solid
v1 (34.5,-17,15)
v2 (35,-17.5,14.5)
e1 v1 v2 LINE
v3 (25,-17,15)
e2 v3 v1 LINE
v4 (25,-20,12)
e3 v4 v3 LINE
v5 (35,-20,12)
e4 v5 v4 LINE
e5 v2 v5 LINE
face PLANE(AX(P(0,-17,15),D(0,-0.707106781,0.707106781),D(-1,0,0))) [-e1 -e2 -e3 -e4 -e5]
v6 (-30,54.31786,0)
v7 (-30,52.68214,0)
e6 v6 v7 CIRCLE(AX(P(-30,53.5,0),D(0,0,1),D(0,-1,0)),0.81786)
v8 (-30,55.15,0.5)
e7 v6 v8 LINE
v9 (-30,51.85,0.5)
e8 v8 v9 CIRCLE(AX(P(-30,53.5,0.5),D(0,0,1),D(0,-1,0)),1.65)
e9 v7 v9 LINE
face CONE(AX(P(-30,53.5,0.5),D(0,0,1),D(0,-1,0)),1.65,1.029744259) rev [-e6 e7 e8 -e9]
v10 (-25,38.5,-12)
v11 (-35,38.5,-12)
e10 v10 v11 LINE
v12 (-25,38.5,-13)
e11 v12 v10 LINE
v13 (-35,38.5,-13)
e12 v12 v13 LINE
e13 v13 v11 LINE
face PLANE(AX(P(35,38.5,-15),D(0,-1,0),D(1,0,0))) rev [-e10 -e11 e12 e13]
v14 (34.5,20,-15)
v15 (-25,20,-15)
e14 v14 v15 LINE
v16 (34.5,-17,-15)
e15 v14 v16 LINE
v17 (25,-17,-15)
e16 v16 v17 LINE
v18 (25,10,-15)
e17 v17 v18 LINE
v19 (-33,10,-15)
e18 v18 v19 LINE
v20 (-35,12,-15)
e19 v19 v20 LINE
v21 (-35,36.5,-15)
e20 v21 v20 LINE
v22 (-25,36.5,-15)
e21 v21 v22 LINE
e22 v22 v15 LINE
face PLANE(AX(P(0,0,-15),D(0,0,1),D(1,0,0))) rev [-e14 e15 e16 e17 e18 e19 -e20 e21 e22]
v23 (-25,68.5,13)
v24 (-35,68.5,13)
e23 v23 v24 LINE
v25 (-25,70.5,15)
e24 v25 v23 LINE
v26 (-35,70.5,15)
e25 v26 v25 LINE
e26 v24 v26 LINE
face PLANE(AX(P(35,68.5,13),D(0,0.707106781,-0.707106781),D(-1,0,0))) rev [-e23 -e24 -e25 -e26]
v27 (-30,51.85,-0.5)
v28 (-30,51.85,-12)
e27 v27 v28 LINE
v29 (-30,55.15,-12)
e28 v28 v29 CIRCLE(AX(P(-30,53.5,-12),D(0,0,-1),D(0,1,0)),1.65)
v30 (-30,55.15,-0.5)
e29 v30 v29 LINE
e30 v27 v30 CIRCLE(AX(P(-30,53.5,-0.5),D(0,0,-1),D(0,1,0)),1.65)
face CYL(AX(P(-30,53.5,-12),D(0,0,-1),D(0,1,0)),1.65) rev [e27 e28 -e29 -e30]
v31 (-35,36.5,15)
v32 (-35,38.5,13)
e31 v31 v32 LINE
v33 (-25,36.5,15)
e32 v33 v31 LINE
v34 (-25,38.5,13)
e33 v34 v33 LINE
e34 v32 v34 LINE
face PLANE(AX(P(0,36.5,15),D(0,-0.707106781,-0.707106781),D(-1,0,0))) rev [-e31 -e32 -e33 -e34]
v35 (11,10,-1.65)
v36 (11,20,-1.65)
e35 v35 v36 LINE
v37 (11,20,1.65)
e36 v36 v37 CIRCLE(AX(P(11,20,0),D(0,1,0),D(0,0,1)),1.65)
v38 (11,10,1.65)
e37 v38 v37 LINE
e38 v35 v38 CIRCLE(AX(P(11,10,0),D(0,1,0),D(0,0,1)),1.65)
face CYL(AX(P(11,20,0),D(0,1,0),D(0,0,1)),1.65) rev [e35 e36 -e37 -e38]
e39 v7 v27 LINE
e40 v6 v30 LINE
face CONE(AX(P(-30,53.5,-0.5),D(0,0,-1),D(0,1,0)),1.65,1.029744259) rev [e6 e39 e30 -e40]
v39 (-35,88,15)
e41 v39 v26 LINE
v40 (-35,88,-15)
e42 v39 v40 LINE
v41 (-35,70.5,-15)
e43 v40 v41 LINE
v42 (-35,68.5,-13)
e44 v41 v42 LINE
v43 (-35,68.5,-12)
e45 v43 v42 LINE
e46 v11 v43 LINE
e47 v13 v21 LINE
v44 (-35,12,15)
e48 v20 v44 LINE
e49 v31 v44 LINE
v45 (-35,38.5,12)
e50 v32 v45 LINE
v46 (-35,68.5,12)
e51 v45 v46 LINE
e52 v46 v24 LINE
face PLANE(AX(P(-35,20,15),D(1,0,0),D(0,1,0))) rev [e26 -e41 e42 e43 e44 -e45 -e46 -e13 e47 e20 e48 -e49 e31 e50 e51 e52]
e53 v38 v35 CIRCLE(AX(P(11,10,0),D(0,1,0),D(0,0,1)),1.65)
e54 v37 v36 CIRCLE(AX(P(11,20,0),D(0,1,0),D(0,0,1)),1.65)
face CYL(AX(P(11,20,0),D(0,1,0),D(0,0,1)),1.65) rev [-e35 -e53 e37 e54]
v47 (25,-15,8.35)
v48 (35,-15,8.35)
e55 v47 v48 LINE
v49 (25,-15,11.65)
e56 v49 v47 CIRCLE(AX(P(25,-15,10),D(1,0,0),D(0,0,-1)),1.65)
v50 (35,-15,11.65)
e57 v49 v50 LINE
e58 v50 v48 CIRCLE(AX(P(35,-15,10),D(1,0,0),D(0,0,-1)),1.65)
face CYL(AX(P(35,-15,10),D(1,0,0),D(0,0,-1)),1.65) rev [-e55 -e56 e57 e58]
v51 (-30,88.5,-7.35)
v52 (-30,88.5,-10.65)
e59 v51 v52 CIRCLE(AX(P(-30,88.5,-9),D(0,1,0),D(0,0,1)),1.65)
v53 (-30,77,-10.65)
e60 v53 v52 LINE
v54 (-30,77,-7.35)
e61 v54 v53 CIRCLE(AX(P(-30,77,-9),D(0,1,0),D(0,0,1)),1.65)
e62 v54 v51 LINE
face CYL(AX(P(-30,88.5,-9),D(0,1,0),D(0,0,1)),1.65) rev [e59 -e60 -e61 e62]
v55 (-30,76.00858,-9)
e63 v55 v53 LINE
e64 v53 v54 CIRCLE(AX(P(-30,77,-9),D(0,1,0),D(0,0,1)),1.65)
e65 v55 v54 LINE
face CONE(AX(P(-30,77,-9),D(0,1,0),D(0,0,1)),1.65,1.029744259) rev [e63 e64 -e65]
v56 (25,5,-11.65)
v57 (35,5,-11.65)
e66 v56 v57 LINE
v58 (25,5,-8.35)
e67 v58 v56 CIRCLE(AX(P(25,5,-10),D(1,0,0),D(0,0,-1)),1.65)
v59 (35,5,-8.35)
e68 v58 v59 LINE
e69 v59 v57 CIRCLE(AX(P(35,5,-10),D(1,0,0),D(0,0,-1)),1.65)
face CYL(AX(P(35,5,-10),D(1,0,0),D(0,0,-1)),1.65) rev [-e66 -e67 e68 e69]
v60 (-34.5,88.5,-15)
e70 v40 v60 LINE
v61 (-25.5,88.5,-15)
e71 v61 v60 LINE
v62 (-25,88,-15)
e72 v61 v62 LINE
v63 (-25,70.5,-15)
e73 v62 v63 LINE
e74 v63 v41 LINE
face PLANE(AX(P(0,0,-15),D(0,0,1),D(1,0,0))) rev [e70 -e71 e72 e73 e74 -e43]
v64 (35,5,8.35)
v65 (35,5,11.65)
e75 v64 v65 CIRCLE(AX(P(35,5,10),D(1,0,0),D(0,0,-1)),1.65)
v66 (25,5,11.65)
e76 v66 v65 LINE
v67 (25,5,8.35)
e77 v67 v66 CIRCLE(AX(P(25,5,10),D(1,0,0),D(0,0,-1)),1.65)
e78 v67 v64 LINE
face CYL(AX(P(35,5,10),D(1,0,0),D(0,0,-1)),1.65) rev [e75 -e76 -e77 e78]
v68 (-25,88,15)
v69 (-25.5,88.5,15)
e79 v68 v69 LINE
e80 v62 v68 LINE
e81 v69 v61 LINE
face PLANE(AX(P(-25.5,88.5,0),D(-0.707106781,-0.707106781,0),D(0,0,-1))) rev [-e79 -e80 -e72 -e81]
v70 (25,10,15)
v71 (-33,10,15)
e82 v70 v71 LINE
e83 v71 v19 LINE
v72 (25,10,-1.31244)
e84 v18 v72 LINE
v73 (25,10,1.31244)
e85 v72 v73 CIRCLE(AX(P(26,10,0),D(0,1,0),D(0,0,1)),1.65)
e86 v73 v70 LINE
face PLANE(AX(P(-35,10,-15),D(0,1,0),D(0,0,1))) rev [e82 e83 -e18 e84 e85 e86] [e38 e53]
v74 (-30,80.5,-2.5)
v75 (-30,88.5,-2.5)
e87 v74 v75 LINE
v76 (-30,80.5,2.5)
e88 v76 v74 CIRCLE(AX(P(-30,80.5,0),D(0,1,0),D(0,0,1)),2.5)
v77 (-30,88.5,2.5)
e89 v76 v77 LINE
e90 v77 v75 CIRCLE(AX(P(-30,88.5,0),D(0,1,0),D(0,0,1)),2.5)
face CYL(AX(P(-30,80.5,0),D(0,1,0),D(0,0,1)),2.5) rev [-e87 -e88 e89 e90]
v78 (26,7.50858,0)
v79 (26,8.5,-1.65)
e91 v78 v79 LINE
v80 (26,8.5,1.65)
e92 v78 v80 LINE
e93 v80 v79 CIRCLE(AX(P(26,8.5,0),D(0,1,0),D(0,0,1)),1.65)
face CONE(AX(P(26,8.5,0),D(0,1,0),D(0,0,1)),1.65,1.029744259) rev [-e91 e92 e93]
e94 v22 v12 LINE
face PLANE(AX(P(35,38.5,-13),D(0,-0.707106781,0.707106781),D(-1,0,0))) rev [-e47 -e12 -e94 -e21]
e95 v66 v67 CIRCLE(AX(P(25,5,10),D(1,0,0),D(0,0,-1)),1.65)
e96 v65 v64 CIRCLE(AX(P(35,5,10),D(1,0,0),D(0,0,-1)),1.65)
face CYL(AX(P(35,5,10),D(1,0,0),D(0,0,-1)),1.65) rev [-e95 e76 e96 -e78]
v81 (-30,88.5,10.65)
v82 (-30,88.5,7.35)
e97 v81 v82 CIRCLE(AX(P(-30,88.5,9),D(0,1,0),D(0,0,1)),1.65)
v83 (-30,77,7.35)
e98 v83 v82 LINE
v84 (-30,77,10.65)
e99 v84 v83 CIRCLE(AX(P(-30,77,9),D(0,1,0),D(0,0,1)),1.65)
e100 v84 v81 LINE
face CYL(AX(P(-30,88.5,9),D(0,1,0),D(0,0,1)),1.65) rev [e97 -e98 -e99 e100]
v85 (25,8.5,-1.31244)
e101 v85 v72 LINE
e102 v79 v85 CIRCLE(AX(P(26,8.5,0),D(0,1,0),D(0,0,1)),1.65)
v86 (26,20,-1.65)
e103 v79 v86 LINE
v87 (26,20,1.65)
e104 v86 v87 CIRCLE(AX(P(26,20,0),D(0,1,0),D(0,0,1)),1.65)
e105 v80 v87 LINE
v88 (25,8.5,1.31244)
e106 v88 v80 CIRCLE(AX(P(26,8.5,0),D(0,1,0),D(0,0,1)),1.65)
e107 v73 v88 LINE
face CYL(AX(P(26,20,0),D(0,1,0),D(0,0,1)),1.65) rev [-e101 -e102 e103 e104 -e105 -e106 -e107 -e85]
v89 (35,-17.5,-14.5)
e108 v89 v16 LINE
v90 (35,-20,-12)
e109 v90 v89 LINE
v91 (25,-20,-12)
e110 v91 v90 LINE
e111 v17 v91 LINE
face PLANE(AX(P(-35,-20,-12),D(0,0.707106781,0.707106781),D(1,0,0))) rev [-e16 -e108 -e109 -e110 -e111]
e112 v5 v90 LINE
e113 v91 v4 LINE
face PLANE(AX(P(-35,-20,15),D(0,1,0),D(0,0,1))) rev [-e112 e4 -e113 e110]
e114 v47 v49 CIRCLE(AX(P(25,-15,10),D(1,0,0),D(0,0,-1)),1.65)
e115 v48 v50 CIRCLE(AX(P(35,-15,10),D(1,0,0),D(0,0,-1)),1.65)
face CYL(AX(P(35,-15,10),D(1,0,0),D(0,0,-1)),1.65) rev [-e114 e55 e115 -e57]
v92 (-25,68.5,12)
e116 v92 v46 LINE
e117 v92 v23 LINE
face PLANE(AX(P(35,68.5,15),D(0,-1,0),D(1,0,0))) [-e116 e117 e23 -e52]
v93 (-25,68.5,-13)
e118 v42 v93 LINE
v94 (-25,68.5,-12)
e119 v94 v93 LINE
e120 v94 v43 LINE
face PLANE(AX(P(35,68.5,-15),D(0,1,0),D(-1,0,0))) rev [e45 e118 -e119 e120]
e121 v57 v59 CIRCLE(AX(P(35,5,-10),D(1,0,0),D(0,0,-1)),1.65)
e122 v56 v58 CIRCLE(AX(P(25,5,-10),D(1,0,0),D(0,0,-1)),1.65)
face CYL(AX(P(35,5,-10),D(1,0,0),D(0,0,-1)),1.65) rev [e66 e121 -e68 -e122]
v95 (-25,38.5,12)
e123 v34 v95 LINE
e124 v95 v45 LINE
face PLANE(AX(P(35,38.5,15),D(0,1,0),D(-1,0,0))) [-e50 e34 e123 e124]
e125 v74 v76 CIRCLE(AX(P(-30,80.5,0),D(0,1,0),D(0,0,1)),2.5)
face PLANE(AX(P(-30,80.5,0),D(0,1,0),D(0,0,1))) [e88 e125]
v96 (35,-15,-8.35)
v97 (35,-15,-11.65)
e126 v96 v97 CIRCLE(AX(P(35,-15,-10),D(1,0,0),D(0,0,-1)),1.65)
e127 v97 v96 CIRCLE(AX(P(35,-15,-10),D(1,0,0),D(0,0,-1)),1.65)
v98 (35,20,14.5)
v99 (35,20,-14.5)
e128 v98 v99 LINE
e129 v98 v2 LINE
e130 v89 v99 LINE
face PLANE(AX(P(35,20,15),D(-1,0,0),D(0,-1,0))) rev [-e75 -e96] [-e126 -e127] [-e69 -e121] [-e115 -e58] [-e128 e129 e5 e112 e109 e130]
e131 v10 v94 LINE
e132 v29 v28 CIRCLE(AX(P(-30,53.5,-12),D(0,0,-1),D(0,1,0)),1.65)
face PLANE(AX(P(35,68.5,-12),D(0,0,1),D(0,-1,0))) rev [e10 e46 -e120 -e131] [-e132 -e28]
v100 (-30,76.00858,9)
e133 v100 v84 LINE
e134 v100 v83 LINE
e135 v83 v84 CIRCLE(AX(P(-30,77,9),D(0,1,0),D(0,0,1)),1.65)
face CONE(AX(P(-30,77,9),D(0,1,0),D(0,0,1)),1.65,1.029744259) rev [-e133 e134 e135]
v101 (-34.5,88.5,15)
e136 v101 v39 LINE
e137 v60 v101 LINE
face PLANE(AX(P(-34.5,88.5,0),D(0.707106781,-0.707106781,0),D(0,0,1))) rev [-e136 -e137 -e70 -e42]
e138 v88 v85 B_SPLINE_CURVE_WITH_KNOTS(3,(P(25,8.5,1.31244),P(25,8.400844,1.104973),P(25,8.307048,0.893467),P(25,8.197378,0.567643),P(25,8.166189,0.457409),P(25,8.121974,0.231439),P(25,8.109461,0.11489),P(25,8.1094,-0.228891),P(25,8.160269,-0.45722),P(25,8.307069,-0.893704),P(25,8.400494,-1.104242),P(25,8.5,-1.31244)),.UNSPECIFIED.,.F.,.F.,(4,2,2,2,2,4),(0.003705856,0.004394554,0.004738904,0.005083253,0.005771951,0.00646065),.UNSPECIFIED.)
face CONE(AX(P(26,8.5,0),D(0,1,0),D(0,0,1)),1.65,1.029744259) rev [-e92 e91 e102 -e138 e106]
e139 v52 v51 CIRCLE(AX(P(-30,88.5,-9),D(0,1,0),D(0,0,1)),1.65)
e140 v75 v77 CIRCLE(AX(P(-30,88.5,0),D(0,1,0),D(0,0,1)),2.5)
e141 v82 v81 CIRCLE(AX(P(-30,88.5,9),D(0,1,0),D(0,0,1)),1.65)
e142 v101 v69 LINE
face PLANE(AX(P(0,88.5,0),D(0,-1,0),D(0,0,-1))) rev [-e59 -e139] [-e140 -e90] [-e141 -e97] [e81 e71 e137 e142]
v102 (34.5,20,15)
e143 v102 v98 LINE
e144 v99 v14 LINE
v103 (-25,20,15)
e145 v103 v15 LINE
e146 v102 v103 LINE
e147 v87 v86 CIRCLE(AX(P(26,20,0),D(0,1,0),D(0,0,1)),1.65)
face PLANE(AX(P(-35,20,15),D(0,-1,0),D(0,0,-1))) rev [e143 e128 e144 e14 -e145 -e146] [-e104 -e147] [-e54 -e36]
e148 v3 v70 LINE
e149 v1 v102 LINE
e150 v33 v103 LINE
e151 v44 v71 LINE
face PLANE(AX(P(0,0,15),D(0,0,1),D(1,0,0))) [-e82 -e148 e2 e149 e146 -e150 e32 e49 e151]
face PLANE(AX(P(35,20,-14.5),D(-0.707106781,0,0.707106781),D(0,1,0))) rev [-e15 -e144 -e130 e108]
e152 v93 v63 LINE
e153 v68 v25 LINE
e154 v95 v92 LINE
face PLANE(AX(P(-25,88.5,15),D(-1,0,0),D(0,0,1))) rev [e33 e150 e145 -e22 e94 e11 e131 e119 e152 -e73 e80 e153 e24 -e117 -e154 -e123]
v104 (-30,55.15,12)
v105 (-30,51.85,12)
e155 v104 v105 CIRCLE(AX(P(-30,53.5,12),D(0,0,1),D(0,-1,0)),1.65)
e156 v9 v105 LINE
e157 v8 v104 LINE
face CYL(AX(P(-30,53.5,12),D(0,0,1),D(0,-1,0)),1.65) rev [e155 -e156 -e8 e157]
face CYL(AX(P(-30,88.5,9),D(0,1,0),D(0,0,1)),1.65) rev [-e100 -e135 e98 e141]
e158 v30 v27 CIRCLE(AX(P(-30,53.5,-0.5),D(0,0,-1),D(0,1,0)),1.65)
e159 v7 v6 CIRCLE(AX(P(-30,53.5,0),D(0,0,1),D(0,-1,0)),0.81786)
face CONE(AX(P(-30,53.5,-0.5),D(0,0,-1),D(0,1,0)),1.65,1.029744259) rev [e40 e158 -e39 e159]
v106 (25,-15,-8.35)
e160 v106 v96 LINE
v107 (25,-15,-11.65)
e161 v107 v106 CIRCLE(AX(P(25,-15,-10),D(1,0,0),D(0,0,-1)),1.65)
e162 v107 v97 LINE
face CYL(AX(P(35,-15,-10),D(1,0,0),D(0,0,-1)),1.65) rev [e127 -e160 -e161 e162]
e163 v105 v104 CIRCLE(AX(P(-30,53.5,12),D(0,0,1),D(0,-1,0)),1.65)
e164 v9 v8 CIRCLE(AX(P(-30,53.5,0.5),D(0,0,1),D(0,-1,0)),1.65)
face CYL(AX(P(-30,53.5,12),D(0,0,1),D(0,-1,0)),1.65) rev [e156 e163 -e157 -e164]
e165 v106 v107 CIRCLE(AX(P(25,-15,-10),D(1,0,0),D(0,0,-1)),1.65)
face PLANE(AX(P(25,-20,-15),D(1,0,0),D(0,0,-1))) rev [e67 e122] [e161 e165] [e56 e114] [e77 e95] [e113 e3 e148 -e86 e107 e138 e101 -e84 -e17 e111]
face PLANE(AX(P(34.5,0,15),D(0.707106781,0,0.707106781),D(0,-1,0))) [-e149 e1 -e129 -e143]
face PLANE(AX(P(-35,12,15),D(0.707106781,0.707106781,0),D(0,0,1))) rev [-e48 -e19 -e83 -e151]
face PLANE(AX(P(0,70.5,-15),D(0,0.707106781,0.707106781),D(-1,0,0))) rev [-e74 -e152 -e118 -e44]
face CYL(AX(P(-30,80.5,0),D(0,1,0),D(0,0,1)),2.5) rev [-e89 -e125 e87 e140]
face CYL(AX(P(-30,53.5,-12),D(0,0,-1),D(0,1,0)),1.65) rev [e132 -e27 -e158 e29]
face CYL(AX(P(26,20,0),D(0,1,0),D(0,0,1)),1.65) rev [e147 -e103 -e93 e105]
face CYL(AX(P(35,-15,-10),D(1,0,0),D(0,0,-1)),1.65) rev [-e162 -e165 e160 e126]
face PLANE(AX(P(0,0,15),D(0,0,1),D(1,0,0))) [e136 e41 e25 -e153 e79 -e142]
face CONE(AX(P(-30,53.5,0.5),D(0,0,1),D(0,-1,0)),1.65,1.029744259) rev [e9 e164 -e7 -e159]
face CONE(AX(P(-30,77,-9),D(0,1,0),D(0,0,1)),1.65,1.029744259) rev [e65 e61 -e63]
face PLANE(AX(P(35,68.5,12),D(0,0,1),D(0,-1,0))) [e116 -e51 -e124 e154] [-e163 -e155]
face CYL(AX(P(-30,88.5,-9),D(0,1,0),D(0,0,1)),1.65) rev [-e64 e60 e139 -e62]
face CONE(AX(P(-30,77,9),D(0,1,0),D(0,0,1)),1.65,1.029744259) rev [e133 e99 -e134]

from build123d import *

# Parameters (mm, degrees)
SKETCH1_W             = 70
SKETCH1_H             = 40
BOSS_EXTRUDE1_DEPTH   = 15
SKETCH2_W             = 60
SKETCH2_H             = 30
CUT_EXTRUDE1_DEPTH    = 51.249378106
CHAMFER1_SIZE         = 0.5
M4_TAPPED_HOLE1_D     = 3.3
M4_TAPPED_HOLE1_DEPTH = 11.5
M4_TAPPED_HOLE1_TIP   = 0.991420021
M4_TAPPED_HOLE2_D     = 3.3
CHAMFER3_SIZE         = 3
SKETCH17_W            = 10
SKETCH17_H            = 30
BOSS_EXTRUDE2_DEPTH   = 68.5
CHAMFER4_SIZE         = 0.5
M4_TAPPED_HOLE3_D     = 3.3
M4_TAPPED_HOLE3_DEPTH = 11.5
M4_TAPPED_HOLE3_TIP   = 0.991420021
CHAMFER5_SIZE         = 2
SKETCH20_R            = 2.5
CUT_EXTRUDE2_DEPTH    = 8
SKETCH21_W            = 3
SKETCH21_H            = 30
CUT_EXTRUDE3_DEPTH    = 114.829916981
CHAMFER6_SIZE         = 2


with BuildPart() as part:
    # Sketch1 → Boss-Extrude1 (new, symmetric)
    with BuildSketch(Plane.XY):
        Rectangle(SKETCH1_W, SKETCH1_H)
    extrude(amount=BOSS_EXTRUDE1_DEPTH, both=True)

    # Sketch2 → Cut-Extrude1 (cut, through all)
    with BuildSketch(Plane.XY.offset(15)):
        with Locations((-5, -5)):
            Rectangle(SKETCH2_W, SKETCH2_H)
    extrude(amount=-CUT_EXTRUDE1_DEPTH, mode=Mode.SUBTRACT)

    # Chamfer1
    chamfer1_edges = [part.edges().sort_by_distance(p)[0] for p in [
        (35, 0, 15),
        (35, 0, -15),
    ]]
    chamfer(chamfer1_edges, length=CHAMFER1_SIZE)

    # M4 Tapped Hole1
    with Locations(Plane(origin=(0, 20, 0), x_dir=(1, 0, 0), z_dir=(0, 1, 0))):
        with Locations((11, 0), (26, 0)):
            Hole(M4_TAPPED_HOLE1_D / 2, depth=M4_TAPPED_HOLE1_DEPTH)
            with Locations((0, 0, -(M4_TAPPED_HOLE1_DEPTH + M4_TAPPED_HOLE1_TIP / 2))):  # 118° drill point
                Cone(0, M4_TAPPED_HOLE1_D / 2, M4_TAPPED_HOLE1_TIP, mode=Mode.SUBTRACT)

    # M4 Tapped Hole2 (through all)
    with Locations(Plane(origin=(35, 0, 0), x_dir=(0, 0, -1), z_dir=(1, 0, 0))):
        with Locations((-10, 5), (-10, -15), (10, -15), (10, 5)):
            Hole(M4_TAPPED_HOLE2_D / 2)

    # Chamfer3
    chamfer3_edges = [part.edges().sort_by_distance(p)[0] for p in [
        (29.75, -20, -15),
        (29.75, -20, 15),
    ]]
    chamfer(chamfer3_edges, length=CHAMFER3_SIZE)

    # Sketch17 → Boss-Extrude2 (add)
    with BuildSketch(Plane(origin=(0, 20, 0), x_dir=(1, 0, 0), z_dir=(0, 1, 0))):
        with Locations((-30, 0)):
            Rectangle(SKETCH17_W, SKETCH17_H)
    extrude(amount=BOSS_EXTRUDE2_DEPTH)

    # Chamfer4
    chamfer4_edges = [part.edges().sort_by_distance(p)[0] for p in [
        (-25, 88.5, 0),
        (-35, 88.5, 0),
    ]]
    chamfer(chamfer4_edges, length=CHAMFER4_SIZE)

    # M4 Tapped Hole3
    with Locations(Plane(origin=(0, 88.5, 0), x_dir=(1, 0, 0), z_dir=(0, 1, 0))):
        with Locations((-30, 9), (-30, -9)):
            Hole(M4_TAPPED_HOLE3_D / 2, depth=M4_TAPPED_HOLE3_DEPTH)
            with Locations((0, 0, -(M4_TAPPED_HOLE3_DEPTH + M4_TAPPED_HOLE3_TIP / 2))):  # 118° drill point
                Cone(0, M4_TAPPED_HOLE3_D / 2, M4_TAPPED_HOLE3_TIP, mode=Mode.SUBTRACT)

    # Chamfer5
    chamfer5_edges = [part.edges().sort_by_distance(p)[0] for p in [
        (-35, 10, 0),
    ]]
    chamfer(chamfer5_edges, length=CHAMFER5_SIZE)

    # Sketch20 → Cut-Extrude2 (cut)
    with BuildSketch(Plane(origin=(0, 88.5, 0), x_dir=(1, 0, 0), z_dir=(0, 1, 0))):
        with Locations(Location((-30, 0, 0), (0, 0, 270))):
            Circle(SKETCH20_R)
    extrude(amount=-CUT_EXTRUDE2_DEPTH, mode=Mode.SUBTRACT)

    # Sketch21 → Cut-Extrude3 (cut, through all)
    with BuildSketch(Plane.ZY.offset(35)):
        with Locations((-13.5, 53.5)):
            Rectangle(SKETCH21_W, SKETCH21_H)
    cut_extrude3 = extrude(amount=-CUT_EXTRUDE3_DEPTH, mode=Mode.SUBTRACT)

    # Sketch22 → M4 Tapped Hole4 (revolve, cut)
    with BuildSketch(Plane(origin=(-30, 53.5, -12), x_dir=(0, 1, 0), z_dir=(1, 0, 0))):
        Polygon((0, 0), (0, 12.491420021), (1.65, 11.5), (1.65, 0), align=None)
    m4_tapped_hole4 = revolve(axis=Axis((-30, 53.5, -18.35), (0, 0, 1)), mode=Mode.SUBTRACT)

    # Mirror2: Cut-Extrude3, M4 Tapped Hole4 across plane
    add(cut_extrude3.mirror(Plane.XY), mode=Mode.SUBTRACT)
    add(m4_tapped_hole4.mirror(Plane.XY), mode=Mode.SUBTRACT)

    # Chamfer6
    chamfer6_edges = [part.edges().sort_by_distance(p)[0] for p in [
        (-30, 38.5, -15),
        (-30, 68.5, -15),
        (-30, 68.5, 15),
        (-30, 38.5, 15),
    ]]
    chamfer(chamfer6_edges, length=CHAMFER6_SIZE)


solid = part.part
